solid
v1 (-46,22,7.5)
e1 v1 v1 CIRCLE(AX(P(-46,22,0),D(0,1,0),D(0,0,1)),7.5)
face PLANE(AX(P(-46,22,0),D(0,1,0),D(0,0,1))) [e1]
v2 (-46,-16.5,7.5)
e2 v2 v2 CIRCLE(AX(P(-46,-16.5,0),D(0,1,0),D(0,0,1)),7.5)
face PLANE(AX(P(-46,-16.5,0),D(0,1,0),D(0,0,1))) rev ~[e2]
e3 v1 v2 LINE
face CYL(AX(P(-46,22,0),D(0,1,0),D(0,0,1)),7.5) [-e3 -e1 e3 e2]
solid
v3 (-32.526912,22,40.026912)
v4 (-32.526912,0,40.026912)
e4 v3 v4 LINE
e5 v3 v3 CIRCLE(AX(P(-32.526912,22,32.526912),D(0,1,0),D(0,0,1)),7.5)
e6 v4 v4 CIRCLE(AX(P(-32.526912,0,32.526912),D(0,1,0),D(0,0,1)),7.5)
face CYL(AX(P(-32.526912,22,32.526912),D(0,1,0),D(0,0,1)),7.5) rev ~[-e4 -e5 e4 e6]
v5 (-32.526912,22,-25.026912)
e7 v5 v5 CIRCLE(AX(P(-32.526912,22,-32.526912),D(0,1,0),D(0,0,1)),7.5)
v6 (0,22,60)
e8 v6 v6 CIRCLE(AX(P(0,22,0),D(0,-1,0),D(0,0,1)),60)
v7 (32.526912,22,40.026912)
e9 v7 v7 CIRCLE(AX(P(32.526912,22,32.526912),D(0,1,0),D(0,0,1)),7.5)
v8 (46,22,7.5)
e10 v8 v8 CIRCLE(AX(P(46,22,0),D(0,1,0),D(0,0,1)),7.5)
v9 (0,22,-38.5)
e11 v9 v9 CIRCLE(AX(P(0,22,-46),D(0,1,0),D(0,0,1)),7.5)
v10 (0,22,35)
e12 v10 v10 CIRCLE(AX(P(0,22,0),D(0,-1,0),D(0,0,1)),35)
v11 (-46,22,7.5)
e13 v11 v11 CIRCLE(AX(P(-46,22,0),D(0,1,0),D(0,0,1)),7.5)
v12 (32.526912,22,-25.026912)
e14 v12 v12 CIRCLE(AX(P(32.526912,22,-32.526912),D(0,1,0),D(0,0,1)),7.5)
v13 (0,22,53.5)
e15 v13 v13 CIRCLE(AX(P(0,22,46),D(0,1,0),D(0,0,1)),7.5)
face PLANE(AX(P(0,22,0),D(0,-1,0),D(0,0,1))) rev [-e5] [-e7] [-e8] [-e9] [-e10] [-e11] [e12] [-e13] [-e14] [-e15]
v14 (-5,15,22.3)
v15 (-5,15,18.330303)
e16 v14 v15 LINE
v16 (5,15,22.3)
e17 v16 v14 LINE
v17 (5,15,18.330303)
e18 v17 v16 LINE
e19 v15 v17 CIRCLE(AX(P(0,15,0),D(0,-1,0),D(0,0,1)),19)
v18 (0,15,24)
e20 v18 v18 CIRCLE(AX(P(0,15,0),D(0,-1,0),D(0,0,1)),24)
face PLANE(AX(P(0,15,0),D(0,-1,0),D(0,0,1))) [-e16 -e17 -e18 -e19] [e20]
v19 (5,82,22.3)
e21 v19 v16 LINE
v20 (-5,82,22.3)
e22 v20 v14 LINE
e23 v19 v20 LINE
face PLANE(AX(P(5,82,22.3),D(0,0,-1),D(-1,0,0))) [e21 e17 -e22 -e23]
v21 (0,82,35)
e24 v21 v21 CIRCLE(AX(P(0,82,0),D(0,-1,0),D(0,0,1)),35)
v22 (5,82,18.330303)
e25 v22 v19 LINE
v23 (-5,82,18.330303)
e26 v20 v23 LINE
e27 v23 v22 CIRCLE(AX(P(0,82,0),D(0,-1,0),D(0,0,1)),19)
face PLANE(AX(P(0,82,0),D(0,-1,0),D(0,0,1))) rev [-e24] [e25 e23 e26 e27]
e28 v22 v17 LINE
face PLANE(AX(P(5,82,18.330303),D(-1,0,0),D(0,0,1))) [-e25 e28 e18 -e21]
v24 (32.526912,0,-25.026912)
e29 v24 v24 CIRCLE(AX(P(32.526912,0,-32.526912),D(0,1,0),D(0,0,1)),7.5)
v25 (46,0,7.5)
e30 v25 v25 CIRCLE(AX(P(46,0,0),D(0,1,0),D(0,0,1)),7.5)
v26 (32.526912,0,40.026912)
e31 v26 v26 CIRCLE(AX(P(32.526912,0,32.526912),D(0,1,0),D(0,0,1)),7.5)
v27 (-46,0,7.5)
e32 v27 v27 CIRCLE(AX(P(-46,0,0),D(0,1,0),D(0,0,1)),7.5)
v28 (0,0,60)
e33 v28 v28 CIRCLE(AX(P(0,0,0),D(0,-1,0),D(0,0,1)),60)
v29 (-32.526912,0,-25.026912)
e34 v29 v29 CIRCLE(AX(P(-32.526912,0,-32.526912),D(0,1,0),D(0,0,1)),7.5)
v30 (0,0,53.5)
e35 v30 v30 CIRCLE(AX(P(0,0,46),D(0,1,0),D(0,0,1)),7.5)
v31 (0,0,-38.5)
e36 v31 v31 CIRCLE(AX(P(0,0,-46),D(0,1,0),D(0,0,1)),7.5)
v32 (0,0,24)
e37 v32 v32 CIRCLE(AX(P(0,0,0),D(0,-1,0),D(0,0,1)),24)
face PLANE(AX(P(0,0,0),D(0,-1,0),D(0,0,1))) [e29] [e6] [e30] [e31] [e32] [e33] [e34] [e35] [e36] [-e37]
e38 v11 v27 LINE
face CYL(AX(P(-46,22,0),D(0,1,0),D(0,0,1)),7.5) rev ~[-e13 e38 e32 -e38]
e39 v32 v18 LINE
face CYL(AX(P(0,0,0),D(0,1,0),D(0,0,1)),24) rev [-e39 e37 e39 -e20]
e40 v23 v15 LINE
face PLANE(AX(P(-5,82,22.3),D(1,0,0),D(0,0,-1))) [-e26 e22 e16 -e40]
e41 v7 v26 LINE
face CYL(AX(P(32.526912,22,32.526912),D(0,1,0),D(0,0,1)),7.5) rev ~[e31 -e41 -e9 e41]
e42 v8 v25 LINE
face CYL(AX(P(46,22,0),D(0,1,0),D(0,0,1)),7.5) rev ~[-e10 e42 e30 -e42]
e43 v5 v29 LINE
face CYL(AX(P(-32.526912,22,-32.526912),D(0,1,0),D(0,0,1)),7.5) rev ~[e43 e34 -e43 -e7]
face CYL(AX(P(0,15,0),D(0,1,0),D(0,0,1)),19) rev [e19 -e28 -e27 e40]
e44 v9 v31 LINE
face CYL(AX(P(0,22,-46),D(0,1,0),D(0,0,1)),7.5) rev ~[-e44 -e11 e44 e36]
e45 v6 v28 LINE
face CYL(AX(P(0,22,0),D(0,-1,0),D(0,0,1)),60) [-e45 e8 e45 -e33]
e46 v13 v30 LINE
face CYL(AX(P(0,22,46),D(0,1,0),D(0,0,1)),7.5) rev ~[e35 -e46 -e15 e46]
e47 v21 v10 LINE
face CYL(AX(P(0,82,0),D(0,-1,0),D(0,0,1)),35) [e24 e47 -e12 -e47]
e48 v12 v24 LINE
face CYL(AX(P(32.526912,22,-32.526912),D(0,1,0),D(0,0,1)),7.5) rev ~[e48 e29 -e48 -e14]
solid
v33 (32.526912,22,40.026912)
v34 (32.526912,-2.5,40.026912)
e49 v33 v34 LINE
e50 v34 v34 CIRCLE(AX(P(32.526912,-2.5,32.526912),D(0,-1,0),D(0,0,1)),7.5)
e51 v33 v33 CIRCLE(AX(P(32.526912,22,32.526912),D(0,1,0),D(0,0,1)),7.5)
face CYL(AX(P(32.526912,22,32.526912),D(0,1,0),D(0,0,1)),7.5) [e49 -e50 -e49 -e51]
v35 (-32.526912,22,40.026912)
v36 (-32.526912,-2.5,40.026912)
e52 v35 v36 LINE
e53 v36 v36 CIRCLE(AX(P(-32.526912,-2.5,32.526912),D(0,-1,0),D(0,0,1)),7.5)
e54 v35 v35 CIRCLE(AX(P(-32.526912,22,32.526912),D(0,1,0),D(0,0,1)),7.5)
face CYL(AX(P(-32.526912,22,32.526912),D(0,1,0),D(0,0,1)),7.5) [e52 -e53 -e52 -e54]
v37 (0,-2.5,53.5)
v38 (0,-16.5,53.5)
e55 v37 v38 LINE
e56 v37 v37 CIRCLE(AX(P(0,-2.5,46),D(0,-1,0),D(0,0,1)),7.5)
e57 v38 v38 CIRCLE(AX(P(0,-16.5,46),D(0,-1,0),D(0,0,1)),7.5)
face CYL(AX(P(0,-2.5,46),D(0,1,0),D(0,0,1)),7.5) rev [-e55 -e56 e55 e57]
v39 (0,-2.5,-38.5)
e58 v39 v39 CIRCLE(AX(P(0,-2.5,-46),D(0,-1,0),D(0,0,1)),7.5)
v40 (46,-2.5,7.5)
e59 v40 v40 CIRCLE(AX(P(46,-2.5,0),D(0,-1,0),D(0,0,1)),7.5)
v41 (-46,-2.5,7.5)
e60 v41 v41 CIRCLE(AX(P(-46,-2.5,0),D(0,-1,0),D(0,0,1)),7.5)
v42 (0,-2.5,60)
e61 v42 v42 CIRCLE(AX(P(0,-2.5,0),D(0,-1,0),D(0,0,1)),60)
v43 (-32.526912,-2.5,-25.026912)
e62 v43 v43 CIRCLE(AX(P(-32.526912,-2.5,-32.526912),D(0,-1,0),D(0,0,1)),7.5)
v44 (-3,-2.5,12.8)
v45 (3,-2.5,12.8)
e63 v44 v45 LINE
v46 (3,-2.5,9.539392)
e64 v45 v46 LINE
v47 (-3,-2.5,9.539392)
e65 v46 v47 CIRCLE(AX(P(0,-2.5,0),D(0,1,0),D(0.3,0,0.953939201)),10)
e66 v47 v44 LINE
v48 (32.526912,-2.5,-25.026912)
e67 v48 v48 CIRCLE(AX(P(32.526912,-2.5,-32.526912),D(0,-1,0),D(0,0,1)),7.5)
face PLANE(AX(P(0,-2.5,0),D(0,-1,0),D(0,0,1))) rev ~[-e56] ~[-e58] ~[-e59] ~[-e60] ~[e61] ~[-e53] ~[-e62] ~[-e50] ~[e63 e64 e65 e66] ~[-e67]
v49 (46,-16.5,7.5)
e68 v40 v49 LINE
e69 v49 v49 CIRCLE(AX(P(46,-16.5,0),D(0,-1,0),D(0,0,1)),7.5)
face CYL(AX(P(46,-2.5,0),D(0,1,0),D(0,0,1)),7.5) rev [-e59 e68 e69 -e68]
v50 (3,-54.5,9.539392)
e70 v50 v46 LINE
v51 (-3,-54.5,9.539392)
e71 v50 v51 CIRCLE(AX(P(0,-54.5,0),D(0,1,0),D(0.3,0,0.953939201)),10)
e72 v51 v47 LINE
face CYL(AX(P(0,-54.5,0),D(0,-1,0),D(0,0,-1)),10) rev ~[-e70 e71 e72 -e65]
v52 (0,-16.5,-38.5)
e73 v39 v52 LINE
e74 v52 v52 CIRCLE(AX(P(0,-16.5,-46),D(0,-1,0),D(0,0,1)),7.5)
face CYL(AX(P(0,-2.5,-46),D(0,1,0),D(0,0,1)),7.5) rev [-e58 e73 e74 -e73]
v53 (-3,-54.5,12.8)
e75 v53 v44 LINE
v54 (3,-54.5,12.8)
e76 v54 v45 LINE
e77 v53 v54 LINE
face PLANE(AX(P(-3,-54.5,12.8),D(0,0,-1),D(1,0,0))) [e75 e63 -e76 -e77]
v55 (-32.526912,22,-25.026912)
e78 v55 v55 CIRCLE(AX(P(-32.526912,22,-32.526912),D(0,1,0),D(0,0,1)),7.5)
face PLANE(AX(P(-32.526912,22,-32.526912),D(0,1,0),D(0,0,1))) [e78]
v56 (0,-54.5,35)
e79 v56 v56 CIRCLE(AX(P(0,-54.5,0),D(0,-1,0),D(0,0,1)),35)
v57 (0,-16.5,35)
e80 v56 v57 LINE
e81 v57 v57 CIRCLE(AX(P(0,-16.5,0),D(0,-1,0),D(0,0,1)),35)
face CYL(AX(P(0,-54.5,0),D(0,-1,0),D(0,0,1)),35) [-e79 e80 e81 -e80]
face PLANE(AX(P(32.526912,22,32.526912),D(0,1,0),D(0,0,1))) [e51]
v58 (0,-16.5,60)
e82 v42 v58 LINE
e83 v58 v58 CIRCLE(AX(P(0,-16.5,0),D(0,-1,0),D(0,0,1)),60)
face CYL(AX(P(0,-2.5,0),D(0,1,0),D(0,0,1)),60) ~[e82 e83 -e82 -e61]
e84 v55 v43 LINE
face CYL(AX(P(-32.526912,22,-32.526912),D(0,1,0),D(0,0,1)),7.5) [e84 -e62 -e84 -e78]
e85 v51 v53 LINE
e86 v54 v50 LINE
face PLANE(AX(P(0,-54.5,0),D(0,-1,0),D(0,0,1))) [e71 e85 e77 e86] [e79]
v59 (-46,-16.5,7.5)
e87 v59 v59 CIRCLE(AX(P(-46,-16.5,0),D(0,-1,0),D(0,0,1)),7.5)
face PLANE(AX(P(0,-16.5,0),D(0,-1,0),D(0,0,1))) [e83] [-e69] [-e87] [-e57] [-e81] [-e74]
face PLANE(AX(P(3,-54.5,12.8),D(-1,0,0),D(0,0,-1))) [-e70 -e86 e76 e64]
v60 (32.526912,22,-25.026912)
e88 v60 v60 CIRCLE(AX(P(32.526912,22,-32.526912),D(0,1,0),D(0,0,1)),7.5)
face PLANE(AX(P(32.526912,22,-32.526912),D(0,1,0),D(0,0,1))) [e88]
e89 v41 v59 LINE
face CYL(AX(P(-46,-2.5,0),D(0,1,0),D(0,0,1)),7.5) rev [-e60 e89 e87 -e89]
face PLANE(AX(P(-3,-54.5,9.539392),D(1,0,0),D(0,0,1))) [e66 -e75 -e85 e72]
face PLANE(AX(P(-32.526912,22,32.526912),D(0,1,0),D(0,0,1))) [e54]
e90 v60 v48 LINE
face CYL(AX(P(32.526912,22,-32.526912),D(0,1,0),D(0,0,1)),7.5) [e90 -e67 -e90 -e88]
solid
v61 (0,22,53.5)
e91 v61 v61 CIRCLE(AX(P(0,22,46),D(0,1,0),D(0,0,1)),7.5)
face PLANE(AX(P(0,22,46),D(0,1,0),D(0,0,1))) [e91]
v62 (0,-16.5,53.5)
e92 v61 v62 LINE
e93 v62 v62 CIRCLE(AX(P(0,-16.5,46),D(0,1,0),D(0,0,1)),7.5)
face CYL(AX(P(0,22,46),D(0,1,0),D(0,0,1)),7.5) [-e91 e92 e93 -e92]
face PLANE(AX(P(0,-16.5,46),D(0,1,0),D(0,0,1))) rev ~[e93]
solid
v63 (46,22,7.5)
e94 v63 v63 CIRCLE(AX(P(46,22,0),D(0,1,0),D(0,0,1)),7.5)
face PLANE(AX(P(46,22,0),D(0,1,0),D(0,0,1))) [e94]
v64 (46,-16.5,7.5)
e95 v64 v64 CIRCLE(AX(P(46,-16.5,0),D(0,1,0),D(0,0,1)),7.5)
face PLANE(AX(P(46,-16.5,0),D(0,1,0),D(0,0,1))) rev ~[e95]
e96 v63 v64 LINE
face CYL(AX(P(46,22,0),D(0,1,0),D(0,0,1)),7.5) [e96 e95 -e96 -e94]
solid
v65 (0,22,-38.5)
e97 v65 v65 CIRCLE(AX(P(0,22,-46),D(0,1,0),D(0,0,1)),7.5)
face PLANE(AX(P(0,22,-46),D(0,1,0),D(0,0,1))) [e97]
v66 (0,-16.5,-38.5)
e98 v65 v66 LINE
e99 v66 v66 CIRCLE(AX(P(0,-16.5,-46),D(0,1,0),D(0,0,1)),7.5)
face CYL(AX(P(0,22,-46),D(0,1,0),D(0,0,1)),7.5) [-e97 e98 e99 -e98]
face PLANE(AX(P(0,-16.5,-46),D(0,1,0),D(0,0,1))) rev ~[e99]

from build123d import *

# Parameters (mm, degrees)
SKETCH_2_R             = 7.5
CUT_EXTRUDE_1_DEPTH    = 104.923048454
SKETCH_3_R             = 7.5
BOSS_EXTRUDE_1_DEPTH   = 38.5
BOSS_EXTRUDE_1_2_DEPTH = 38.5
BOSS_EXTRUDE_1_3_DEPTH = 38.5
BOSS_EXTRUDE_1_4_DEPTH = 38.5
BOSS_EXTRUDE_1_5_DEPTH = 38.5
BOSS_EXTRUDE_1_6_DEPTH = 38.5
BOSS_EXTRUDE_1_7_DEPTH = 38.5
BOSS_EXTRUDE_1_8_DEPTH = 38.5
BOSS_EXTRUDE_START     = 2.5
SKETCH_4_R             = 60
SKETCH_4_R_2           = 7.5
SKETCH_4_R_3           = 10
BOSS_EXTRUDE_2_DEPTH   = 14
BOSS_EXTRUDE_START_2   = 38
SKETCH_5_R             = 35
SKETCH_5_R_2           = 10
BOSS_EXTRUDE_3_DEPTH   = 38
CUT_EXTRUDE_2_DEPTH    = 52
CUT_EXTRUDE_3_DEPTH    = 67


with BuildPart() as part:
    # Sketch 1 → Revolve 1 (revolve)
    with BuildSketch(Plane.XY, mode=Mode.PRIVATE) as revolve_1_sk:
        Polygon((-19, 15), (-19, 82), (-35, 82), (-35, 22), (-60, 22), (-60, 0), (-24, 0), (-24, 15), align=None)
    revolve(revolve_1_sk.sketch.rotate(Axis((0, 116.572916667, 0), (0, -1, 0)), 270), axis=Axis((0, 116.572916667, 0), (0, -1, 0)))

    # Sketch 2 → Cut-Extrude 1 (cut, through all)
    with BuildSketch(Plane(origin=(0, 22, 0), x_dir=(1, 0, 0), z_dir=(0, 1, 0))):
        with Locations(Location((0, -46, 0), (0, 0, 270))):
            Circle(SKETCH_2_R)
        with Locations(Location((-32.526911935, -32.526911935, 0), (0, 0, 270))):
            Circle(SKETCH_2_R)
        with Locations(Location((-46, 0, 0), (0, 0, 270))):
            Circle(SKETCH_2_R)
        with Locations(Location((-32.526911935, 32.526911935, 0), (0, 0, 270))):
            Circle(SKETCH_2_R)
        with Locations(Location((0, 46, 0), (0, 0, 270))):
            Circle(SKETCH_2_R)
        with Locations(Location((32.526911935, 32.526911935, 0), (0, 0, 270))):
            Circle(SKETCH_2_R)
        with Locations(Location((46, 0, 0), (0, 0, 270))):
            Circle(SKETCH_2_R)
        with Locations(Location((32.526911935, -32.526911935, 0), (0, 0, 270))):
            Circle(SKETCH_2_R)
    extrude(amount=-CUT_EXTRUDE_1_DEPTH, mode=Mode.SUBTRACT)

    # Sketch 7 → Cut-Extrude 3 (cut)
    with BuildSketch(Plane(origin=(0, 82, 0), x_dir=(1, 0, 0), z_dir=(0, 1, 0))):
        with BuildLine():
            Line((5, -18.33030278), (5, -22.3))
            Line((5, -22.3), (-5, -22.3))
            Line((-5, -22.3), (-5, -18.33030278))
            ThreePointArc((-5, -18.33030278), (0, -19), (5, -18.33030278))
        make_face()
    extrude(amount=-CUT_EXTRUDE_3_DEPTH, mode=Mode.SUBTRACT)


with BuildPart() as body_2:
    # Sketch 3 → Boss-Extrude 1 (new body)
    with BuildSketch(Plane(origin=(0, 22, 0), x_dir=(1, 0, 0), z_dir=(0, 1, 0))):
        with Locations(Location((0, -46, 0), (0, 0, 270))):
            Circle(SKETCH_3_R)
    extrude(amount=-BOSS_EXTRUDE_1_DEPTH)


with BuildPart() as body_3:
    # Sketch 3 → Boss-Extrude 1 2 (new body)
    with BuildSketch(Plane(origin=(0, 22, 0), x_dir=(1, 0, 0), z_dir=(0, 1, 0))):
        with Locations(Location((-32.526911935, -32.526911935, 0), (0, 0, 270))):
            Circle(SKETCH_3_R)
    extrude(amount=-BOSS_EXTRUDE_1_2_DEPTH)



with BuildPart() as body_4:
    # Sketch 3 → Boss-Extrude 1 3 (new body)
    with BuildSketch(Plane(origin=(0, 22, 0), x_dir=(1, 0, 0), z_dir=(0, 1, 0))):
        with Locations(Location((-46, 0, 0), (0, 0, 270))):
            Circle(SKETCH_3_R)
    extrude(amount=-BOSS_EXTRUDE_1_3_DEPTH)


with BuildPart() as body_5:
    # Sketch 3 → Boss-Extrude 1 4 (new body)
    with BuildSketch(Plane(origin=(0, 22, 0), x_dir=(1, 0, 0), z_dir=(0, 1, 0))):
        with Locations(Location((-32.526911935, 32.526911935, 0), (0, 0, 270))):
            Circle(SKETCH_3_R)
    extrude(amount=-BOSS_EXTRUDE_1_4_DEPTH)


with BuildPart() as body_6:
    # Sketch 3 → Boss-Extrude 1 5 (new body)
    with BuildSketch(Plane(origin=(0, 22, 0), x_dir=(1, 0, 0), z_dir=(0, 1, 0))):
        with Locations(Location((0, 46, 0), (0, 0, 270))):
            Circle(SKETCH_3_R)
    extrude(amount=-BOSS_EXTRUDE_1_5_DEPTH)


with BuildPart() as body_7:
    # Sketch 3 → Boss-Extrude 1 6 (new body)
    with BuildSketch(Plane(origin=(0, 22, 0), x_dir=(1, 0, 0), z_dir=(0, 1, 0))):
        with Locations(Location((32.526911935, 32.526911935, 0), (0, 0, 270))):
            Circle(SKETCH_3_R)
    extrude(amount=-BOSS_EXTRUDE_1_6_DEPTH)


with BuildPart() as body_8:
    # Sketch 3 → Boss-Extrude 1 7 (new body)
    with BuildSketch(Plane(origin=(0, 22, 0), x_dir=(1, 0, 0), z_dir=(0, 1, 0))):
        with Locations(Location((46, 0, 0), (0, 0, 270))):
            Circle(SKETCH_3_R)
    extrude(amount=-BOSS_EXTRUDE_1_7_DEPTH)


with BuildPart() as body_9:
    # Sketch 3 → Boss-Extrude 1 8 (new body)
    with BuildSketch(Plane(origin=(0, 22, 0), x_dir=(1, 0, 0), z_dir=(0, 1, 0))):
        with Locations(Location((32.526911935, -32.526911935, 0), (0, 0, 270))):
            Circle(SKETCH_3_R)
    extrude(amount=-BOSS_EXTRUDE_1_8_DEPTH)


with BuildPart() as body_10:
    # Sketch 4 → Boss-Extrude 2 (new body)
    with BuildSketch(Plane.XZ.offset(BOSS_EXTRUDE_START)):
        with Locations(Location((0, 0, 0), (0, 0, 90))):
            Circle(SKETCH_4_R)
        with Locations(Location((-32.526911935, 32.526911935, 0), (0, 0, 90))):
            Circle(SKETCH_4_R_2, mode=Mode.SUBTRACT)
        with Locations(Location((-46, 0, 0), (0, 0, 90))):
            Circle(SKETCH_4_R_2, mode=Mode.SUBTRACT)
        with Locations(Location((-32.526911935, -32.526911935, 0), (0, 0, 90))):
            Circle(SKETCH_4_R_2, mode=Mode.SUBTRACT)
        with Locations(Location((0, -46, 0), (0, 0, 90))):
            Circle(SKETCH_4_R_2, mode=Mode.SUBTRACT)
        with Locations(Location((32.526911935, -32.526911935, 0), (0, 0, 90))):
            Circle(SKETCH_4_R_2, mode=Mode.SUBTRACT)
        with Locations(Location((46, 0, 0), (0, 0, 90))):
            Circle(SKETCH_4_R_2, mode=Mode.SUBTRACT)
        with Locations(Location((32.526911935, 32.526911935, 0), (0, 0, 90))):
            Circle(SKETCH_4_R_2, mode=Mode.SUBTRACT)
        with Locations(Location((0, 46, 0), (0, 0, 90))):
            Circle(SKETCH_4_R_2, mode=Mode.SUBTRACT)
        with Locations(Location((0, 0, 0), (0, 0, 270))):
            Circle(SKETCH_4_R_3, mode=Mode.SUBTRACT)
    extrude(amount=BOSS_EXTRUDE_2_DEPTH)


with BuildPart() as body_3_1:
    add(body_3.part)

    add(body_10.part)  # Boss-Extrude 3 merges body 10

    add(body_5.part)  # Boss-Extrude 3 merges body 5

    add(body_7.part)  # Boss-Extrude 3 merges body 7

    add(body_9.part)  # Boss-Extrude 3 merges body 9
    # Sketch 5 → Boss-Extrude 3 (add)
    with BuildSketch(Plane.XZ.offset(16.5).offset(BOSS_EXTRUDE_START_2)):
        with Locations(Location((0, 0, 0), (0, 0, 90))):
            Circle(SKETCH_5_R)
        with Locations(Location((0, 0, 0), (0, 0, 270))):
            Circle(SKETCH_5_R_2, mode=Mode.SUBTRACT)
    extrude(amount=-BOSS_EXTRUDE_3_DEPTH)

    # Sketch 6 → Cut-Extrude 2 (cut)
    with BuildSketch(Plane.XZ.offset(54.5)):
        with BuildLine():
            Line((-3, 9.539392014), (-3, 12.8))
            Line((-3, 12.8), (3, 12.8))
            Line((3, 12.8), (3, 9.539392014))
            ThreePointArc((3, 9.539392014), (0, 10), (-3, 9.539392014))
        make_face()
    extrude(amount=-CUT_EXTRUDE_2_DEPTH, mode=Mode.SUBTRACT)


solid = Compound([part.part, body_2.part, body_4.part, body_6.part, body_8.part, body_3_1.part])
